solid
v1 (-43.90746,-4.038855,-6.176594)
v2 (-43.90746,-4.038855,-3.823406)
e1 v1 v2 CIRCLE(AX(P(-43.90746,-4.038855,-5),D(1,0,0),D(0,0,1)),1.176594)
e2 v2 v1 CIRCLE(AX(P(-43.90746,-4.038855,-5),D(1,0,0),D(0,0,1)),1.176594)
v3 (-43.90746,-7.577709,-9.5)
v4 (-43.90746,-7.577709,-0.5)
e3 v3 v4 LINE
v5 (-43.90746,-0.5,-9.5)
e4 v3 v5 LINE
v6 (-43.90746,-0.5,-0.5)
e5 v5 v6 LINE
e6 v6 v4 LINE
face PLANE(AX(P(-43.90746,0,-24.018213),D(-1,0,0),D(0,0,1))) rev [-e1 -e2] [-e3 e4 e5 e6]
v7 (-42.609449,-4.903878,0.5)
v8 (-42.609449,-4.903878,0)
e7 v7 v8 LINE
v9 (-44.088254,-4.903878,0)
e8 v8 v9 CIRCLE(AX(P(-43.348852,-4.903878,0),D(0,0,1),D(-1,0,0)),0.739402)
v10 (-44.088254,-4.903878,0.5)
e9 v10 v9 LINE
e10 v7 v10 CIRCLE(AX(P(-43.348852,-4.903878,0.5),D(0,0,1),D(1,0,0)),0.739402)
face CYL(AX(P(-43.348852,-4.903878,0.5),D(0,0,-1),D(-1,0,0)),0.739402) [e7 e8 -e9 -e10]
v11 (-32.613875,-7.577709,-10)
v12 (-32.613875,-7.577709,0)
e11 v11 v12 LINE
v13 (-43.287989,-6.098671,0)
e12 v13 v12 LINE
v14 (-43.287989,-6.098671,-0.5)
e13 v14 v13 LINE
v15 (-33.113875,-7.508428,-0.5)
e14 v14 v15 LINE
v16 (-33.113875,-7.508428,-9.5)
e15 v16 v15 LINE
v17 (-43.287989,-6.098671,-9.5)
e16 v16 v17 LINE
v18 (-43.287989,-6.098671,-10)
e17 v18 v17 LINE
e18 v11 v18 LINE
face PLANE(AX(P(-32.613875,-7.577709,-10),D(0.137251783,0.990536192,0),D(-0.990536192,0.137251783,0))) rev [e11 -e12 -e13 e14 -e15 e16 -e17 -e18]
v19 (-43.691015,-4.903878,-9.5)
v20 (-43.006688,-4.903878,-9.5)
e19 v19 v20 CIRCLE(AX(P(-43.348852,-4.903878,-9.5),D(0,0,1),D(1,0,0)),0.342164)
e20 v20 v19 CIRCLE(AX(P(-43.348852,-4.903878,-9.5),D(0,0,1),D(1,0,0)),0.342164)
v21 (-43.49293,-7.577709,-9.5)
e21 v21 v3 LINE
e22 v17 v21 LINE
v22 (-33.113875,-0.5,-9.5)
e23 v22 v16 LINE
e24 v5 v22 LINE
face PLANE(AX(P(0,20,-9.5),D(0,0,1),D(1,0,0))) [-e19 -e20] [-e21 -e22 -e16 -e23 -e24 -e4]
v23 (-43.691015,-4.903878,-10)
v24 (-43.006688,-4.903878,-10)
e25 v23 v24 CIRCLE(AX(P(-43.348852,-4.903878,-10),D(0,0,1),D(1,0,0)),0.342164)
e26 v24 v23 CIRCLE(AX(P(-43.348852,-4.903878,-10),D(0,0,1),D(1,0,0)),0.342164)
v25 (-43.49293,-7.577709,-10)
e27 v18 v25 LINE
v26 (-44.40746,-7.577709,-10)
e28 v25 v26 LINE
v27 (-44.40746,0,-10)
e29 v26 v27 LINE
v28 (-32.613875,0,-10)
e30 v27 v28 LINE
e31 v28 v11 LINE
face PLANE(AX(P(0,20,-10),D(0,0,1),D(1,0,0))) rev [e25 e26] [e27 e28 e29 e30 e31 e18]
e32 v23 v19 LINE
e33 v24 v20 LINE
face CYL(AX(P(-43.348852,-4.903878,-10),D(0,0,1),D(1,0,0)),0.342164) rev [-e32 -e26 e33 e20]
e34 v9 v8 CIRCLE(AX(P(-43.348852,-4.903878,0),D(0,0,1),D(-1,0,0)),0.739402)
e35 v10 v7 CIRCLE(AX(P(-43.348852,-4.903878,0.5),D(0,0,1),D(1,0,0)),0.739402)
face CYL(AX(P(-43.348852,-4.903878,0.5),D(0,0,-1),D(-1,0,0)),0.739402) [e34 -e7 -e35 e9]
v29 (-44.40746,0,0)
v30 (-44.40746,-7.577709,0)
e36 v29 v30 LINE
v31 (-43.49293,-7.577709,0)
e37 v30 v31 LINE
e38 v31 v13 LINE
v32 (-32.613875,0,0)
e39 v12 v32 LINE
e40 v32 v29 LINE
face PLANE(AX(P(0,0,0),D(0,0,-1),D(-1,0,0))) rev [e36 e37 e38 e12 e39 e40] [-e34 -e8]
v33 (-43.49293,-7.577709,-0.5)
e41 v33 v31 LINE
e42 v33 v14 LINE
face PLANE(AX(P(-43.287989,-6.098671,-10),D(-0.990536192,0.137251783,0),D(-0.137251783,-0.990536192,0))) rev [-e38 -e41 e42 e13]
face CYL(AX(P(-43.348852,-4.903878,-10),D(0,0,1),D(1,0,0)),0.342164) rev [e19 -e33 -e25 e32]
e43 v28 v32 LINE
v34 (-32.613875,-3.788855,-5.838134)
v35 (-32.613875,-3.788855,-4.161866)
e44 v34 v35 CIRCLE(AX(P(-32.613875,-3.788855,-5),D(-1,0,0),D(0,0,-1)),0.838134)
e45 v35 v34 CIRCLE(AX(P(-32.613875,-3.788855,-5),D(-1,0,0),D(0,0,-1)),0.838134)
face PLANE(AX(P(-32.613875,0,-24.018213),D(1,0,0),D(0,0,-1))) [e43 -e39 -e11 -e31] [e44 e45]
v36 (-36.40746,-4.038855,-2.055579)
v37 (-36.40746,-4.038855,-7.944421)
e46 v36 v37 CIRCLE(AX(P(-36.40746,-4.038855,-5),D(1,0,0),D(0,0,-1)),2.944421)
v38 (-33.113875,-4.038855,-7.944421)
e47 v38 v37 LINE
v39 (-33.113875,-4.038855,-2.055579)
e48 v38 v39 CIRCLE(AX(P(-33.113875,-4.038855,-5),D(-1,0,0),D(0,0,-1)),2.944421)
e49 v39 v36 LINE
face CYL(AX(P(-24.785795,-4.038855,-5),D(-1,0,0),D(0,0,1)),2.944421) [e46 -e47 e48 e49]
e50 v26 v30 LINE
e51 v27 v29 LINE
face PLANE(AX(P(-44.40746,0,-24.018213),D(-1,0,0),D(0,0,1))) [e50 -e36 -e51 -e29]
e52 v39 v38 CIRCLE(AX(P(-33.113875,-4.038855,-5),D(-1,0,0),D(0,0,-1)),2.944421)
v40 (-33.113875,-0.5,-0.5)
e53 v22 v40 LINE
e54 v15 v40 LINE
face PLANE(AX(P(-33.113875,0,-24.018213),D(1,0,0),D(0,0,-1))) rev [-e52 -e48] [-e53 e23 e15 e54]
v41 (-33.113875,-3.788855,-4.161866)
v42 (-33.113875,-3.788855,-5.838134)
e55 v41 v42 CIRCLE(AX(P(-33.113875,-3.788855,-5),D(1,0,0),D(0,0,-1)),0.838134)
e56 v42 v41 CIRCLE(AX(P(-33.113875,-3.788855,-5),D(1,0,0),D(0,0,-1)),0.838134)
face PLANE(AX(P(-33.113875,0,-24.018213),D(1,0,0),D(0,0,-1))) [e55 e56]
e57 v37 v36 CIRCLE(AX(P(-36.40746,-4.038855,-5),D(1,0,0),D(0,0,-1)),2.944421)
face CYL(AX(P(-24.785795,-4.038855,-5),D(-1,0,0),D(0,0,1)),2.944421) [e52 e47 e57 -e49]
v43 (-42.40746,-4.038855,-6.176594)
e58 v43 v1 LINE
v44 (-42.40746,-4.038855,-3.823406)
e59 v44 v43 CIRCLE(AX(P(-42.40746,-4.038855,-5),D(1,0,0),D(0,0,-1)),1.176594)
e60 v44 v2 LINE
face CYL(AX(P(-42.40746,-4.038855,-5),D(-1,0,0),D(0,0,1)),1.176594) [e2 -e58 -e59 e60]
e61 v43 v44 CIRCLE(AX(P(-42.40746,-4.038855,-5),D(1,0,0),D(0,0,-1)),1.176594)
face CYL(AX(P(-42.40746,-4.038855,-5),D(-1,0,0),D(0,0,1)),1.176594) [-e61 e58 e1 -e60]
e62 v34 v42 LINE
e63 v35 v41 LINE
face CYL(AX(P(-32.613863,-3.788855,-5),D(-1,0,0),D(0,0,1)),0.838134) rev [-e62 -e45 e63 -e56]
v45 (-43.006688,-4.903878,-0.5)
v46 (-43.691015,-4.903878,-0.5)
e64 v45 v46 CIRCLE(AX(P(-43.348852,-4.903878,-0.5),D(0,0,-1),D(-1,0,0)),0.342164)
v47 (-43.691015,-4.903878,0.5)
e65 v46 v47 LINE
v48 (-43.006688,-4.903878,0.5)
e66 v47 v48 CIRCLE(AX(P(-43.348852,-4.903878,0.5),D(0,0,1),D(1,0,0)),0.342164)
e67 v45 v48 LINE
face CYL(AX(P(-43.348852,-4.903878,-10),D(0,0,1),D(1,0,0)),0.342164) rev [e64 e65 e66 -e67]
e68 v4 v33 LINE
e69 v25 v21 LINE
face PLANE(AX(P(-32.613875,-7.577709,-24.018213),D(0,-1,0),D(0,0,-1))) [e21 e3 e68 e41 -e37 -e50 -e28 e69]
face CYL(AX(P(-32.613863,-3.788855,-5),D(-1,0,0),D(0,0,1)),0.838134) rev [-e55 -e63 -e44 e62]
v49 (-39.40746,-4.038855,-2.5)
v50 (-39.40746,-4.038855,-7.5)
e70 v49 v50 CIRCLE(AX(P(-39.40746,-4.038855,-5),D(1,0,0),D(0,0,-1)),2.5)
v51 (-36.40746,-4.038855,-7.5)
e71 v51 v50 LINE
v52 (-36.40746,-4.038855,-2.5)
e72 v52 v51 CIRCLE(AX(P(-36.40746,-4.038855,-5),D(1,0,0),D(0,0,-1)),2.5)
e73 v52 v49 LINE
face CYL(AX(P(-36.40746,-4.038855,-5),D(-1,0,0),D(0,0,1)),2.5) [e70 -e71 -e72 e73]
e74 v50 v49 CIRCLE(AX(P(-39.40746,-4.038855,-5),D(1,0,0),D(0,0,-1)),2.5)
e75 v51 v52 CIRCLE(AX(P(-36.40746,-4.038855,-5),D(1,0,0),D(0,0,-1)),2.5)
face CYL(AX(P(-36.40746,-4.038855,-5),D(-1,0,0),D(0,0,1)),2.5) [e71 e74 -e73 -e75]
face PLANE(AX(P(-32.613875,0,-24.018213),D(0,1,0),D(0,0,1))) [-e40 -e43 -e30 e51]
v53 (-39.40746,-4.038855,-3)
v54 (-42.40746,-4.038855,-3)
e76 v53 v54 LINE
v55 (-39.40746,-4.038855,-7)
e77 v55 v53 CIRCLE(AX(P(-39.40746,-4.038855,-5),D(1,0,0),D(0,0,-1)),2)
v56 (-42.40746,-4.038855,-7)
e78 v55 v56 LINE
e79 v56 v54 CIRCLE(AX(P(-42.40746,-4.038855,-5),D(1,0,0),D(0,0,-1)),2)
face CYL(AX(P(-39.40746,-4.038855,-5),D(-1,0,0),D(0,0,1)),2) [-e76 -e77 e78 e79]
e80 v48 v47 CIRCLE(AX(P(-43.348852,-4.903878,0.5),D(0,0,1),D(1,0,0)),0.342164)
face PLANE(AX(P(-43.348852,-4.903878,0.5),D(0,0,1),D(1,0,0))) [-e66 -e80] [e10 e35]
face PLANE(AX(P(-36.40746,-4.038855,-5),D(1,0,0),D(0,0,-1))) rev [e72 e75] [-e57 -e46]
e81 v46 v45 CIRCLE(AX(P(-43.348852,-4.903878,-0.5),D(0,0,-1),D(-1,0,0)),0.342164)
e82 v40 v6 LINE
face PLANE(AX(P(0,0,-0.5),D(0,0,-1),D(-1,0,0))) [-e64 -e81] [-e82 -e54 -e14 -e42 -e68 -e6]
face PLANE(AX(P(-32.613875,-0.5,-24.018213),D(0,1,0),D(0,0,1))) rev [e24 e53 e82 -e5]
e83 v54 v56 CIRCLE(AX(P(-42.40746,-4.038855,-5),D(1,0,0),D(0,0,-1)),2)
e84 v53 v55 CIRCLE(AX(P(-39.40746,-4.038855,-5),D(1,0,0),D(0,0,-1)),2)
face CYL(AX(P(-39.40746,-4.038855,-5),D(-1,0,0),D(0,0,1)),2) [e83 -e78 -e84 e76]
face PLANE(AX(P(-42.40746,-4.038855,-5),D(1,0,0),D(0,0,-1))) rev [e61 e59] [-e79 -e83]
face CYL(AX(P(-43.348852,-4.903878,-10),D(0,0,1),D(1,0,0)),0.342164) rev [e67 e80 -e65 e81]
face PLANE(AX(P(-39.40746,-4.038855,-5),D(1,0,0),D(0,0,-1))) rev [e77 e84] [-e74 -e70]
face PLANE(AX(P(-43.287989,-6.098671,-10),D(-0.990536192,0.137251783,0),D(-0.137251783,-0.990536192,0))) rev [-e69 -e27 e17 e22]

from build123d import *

# Parameters (mm, degrees)
SKETCH1_W               = 11.793584223
SKETCH1_H               = 7.577709462
BOSS_EXTRUDE1_DEPTH     = 10
SHELL1_T                = -0.5
CUT_EXTRUDE1_DEPTH      = 47.145900644
CUT_EXTRUDE1_DEPTH_BACK = 47.145900644
SKETCH3_R               = 0.739402186
BOSS_EXTRUDE2_DEPTH     = 0.5
CUT_EXTRUDE2_DEPTH      = 47.256828104
CUT_EXTRUDE2_DEPTH_BACK = 47.256828104
SKETCH4_R               = 0.342163572
CUT_EXTRUDE3_DEPTH      = 18.219474717
CUT_EXTRUDE3_DEPTH_BACK = 0.5
SKETCH5_R               = 0.838133872
SKETCH6_R               = 1.176594154
BOSS_EXTRUDE3_DEPTH     = 1.5
SKETCH7_R               = 2
BOSS_EXTRUDE4_DEPTH     = 3
SKETCH8_R               = 2.5
BOSS_EXTRUDE5_DEPTH     = 3
SKETCH9_R               = 2.944420976
BOSS_EXTRUDE6_DEPTH     = 3.293584224


with BuildPart() as part:
    # Sketch1 → Boss-Extrude1 (new body)
    with BuildSketch(Plane.XY):
        with Locations((-38.510667459, -3.788854731)):
            Rectangle(SKETCH1_W, SKETCH1_H)
    extrude(amount=-BOSS_EXTRUDE1_DEPTH)

    # Shell1
    shell1_openings = [part.faces().sort_by_distance(p)[0] for p in [
        (-38.510667459, -7.577709462, -5),
    ]]
    offset(amount=SHELL1_T, openings=shell1_openings, kind=Kind.INTERSECTION)

    # Sketch2 → Cut-Extrude1 (cut, two sides: drawn at the far end of the back side and taken through both)
    with BuildSketch(Plane.XY.offset(-CUT_EXTRUDE1_DEPTH_BACK)):
        Polygon((-32.613875348, -7.577709462), (-43.28798944, -6.09867093), (-43.492929631, -7.577709462), (-42.32222074, -12.914238607), (-34.209763667, -9.465064681), align=None)
    extrude(amount=CUT_EXTRUDE1_DEPTH + CUT_EXTRUDE1_DEPTH_BACK, mode=Mode.SUBTRACT)

    # Sketch3 → Boss-Extrude2 (add)
    with BuildSketch(Plane.XY):
        with Locations(Location((-43.348851562, -4.90387791, 0), (0, 0, 180))):
            Circle(SKETCH3_R)
    extrude(amount=BOSS_EXTRUDE2_DEPTH)

    # Sketch4 → Cut-Extrude2 (cut, two sides: drawn at the far end of the back side and taken through both)
    with BuildSketch(Plane.XY.offset(0.5).offset(-CUT_EXTRUDE2_DEPTH_BACK)):
        with Locations((-43.348851562, -4.90387791)):
            Circle(SKETCH4_R)
    extrude(amount=CUT_EXTRUDE2_DEPTH + CUT_EXTRUDE2_DEPTH_BACK, mode=Mode.SUBTRACT)

    # Sketch5 → Cut-Extrude3 (cut, two sides: drawn at the far end of the back side and taken through both)
    with BuildSketch(Plane(origin=(-32.613875348, 0, 0), x_dir=(0, 0, -1), z_dir=(1, 0, 0)).offset(-CUT_EXTRUDE3_DEPTH_BACK)):
        with Locations(Location((5, -3.788854731, 0), (0, 0, 180))):
            Circle(SKETCH5_R)
    extrude(amount=CUT_EXTRUDE3_DEPTH + CUT_EXTRUDE3_DEPTH_BACK, mode=Mode.SUBTRACT)

    # Sketch6 → Boss-Extrude3 (add)
    with BuildSketch(Plane(origin=(-43.907459571, 0, 0), x_dir=(0, 0, -1), z_dir=(1, 0, 0))):
        with Locations(Location((5, -4.038854731, 0), (0, 0, 180))):
            Circle(SKETCH6_R)
    extrude(amount=BOSS_EXTRUDE3_DEPTH)

    # Sketch7 → Boss-Extrude4 (add)
    with BuildSketch(Plane(origin=(-42.407459571, 0, 0), x_dir=(0, 0, -1), z_dir=(1, 0, 0))):
        with Locations((5, -4.038854731)):
            Circle(SKETCH7_R)
    extrude(amount=BOSS_EXTRUDE4_DEPTH)

    # Sketch8 → Boss-Extrude5 (add)
    with BuildSketch(Plane(origin=(-39.407459571, 0, 0), x_dir=(0, 0, -1), z_dir=(1, 0, 0))):
        with Locations((5, -4.038854731)):
            Circle(SKETCH8_R)
    extrude(amount=BOSS_EXTRUDE5_DEPTH)

    # Sketch9 → Boss-Extrude6 (add)
    with BuildSketch(Plane(origin=(-36.407459571, 0, 0), x_dir=(0, 0, -1), z_dir=(1, 0, 0))):
        with Locations((5, -4.038854731)):
            Circle(SKETCH9_R)
    extrude(amount=BOSS_EXTRUDE6_DEPTH)


solid = part.part
